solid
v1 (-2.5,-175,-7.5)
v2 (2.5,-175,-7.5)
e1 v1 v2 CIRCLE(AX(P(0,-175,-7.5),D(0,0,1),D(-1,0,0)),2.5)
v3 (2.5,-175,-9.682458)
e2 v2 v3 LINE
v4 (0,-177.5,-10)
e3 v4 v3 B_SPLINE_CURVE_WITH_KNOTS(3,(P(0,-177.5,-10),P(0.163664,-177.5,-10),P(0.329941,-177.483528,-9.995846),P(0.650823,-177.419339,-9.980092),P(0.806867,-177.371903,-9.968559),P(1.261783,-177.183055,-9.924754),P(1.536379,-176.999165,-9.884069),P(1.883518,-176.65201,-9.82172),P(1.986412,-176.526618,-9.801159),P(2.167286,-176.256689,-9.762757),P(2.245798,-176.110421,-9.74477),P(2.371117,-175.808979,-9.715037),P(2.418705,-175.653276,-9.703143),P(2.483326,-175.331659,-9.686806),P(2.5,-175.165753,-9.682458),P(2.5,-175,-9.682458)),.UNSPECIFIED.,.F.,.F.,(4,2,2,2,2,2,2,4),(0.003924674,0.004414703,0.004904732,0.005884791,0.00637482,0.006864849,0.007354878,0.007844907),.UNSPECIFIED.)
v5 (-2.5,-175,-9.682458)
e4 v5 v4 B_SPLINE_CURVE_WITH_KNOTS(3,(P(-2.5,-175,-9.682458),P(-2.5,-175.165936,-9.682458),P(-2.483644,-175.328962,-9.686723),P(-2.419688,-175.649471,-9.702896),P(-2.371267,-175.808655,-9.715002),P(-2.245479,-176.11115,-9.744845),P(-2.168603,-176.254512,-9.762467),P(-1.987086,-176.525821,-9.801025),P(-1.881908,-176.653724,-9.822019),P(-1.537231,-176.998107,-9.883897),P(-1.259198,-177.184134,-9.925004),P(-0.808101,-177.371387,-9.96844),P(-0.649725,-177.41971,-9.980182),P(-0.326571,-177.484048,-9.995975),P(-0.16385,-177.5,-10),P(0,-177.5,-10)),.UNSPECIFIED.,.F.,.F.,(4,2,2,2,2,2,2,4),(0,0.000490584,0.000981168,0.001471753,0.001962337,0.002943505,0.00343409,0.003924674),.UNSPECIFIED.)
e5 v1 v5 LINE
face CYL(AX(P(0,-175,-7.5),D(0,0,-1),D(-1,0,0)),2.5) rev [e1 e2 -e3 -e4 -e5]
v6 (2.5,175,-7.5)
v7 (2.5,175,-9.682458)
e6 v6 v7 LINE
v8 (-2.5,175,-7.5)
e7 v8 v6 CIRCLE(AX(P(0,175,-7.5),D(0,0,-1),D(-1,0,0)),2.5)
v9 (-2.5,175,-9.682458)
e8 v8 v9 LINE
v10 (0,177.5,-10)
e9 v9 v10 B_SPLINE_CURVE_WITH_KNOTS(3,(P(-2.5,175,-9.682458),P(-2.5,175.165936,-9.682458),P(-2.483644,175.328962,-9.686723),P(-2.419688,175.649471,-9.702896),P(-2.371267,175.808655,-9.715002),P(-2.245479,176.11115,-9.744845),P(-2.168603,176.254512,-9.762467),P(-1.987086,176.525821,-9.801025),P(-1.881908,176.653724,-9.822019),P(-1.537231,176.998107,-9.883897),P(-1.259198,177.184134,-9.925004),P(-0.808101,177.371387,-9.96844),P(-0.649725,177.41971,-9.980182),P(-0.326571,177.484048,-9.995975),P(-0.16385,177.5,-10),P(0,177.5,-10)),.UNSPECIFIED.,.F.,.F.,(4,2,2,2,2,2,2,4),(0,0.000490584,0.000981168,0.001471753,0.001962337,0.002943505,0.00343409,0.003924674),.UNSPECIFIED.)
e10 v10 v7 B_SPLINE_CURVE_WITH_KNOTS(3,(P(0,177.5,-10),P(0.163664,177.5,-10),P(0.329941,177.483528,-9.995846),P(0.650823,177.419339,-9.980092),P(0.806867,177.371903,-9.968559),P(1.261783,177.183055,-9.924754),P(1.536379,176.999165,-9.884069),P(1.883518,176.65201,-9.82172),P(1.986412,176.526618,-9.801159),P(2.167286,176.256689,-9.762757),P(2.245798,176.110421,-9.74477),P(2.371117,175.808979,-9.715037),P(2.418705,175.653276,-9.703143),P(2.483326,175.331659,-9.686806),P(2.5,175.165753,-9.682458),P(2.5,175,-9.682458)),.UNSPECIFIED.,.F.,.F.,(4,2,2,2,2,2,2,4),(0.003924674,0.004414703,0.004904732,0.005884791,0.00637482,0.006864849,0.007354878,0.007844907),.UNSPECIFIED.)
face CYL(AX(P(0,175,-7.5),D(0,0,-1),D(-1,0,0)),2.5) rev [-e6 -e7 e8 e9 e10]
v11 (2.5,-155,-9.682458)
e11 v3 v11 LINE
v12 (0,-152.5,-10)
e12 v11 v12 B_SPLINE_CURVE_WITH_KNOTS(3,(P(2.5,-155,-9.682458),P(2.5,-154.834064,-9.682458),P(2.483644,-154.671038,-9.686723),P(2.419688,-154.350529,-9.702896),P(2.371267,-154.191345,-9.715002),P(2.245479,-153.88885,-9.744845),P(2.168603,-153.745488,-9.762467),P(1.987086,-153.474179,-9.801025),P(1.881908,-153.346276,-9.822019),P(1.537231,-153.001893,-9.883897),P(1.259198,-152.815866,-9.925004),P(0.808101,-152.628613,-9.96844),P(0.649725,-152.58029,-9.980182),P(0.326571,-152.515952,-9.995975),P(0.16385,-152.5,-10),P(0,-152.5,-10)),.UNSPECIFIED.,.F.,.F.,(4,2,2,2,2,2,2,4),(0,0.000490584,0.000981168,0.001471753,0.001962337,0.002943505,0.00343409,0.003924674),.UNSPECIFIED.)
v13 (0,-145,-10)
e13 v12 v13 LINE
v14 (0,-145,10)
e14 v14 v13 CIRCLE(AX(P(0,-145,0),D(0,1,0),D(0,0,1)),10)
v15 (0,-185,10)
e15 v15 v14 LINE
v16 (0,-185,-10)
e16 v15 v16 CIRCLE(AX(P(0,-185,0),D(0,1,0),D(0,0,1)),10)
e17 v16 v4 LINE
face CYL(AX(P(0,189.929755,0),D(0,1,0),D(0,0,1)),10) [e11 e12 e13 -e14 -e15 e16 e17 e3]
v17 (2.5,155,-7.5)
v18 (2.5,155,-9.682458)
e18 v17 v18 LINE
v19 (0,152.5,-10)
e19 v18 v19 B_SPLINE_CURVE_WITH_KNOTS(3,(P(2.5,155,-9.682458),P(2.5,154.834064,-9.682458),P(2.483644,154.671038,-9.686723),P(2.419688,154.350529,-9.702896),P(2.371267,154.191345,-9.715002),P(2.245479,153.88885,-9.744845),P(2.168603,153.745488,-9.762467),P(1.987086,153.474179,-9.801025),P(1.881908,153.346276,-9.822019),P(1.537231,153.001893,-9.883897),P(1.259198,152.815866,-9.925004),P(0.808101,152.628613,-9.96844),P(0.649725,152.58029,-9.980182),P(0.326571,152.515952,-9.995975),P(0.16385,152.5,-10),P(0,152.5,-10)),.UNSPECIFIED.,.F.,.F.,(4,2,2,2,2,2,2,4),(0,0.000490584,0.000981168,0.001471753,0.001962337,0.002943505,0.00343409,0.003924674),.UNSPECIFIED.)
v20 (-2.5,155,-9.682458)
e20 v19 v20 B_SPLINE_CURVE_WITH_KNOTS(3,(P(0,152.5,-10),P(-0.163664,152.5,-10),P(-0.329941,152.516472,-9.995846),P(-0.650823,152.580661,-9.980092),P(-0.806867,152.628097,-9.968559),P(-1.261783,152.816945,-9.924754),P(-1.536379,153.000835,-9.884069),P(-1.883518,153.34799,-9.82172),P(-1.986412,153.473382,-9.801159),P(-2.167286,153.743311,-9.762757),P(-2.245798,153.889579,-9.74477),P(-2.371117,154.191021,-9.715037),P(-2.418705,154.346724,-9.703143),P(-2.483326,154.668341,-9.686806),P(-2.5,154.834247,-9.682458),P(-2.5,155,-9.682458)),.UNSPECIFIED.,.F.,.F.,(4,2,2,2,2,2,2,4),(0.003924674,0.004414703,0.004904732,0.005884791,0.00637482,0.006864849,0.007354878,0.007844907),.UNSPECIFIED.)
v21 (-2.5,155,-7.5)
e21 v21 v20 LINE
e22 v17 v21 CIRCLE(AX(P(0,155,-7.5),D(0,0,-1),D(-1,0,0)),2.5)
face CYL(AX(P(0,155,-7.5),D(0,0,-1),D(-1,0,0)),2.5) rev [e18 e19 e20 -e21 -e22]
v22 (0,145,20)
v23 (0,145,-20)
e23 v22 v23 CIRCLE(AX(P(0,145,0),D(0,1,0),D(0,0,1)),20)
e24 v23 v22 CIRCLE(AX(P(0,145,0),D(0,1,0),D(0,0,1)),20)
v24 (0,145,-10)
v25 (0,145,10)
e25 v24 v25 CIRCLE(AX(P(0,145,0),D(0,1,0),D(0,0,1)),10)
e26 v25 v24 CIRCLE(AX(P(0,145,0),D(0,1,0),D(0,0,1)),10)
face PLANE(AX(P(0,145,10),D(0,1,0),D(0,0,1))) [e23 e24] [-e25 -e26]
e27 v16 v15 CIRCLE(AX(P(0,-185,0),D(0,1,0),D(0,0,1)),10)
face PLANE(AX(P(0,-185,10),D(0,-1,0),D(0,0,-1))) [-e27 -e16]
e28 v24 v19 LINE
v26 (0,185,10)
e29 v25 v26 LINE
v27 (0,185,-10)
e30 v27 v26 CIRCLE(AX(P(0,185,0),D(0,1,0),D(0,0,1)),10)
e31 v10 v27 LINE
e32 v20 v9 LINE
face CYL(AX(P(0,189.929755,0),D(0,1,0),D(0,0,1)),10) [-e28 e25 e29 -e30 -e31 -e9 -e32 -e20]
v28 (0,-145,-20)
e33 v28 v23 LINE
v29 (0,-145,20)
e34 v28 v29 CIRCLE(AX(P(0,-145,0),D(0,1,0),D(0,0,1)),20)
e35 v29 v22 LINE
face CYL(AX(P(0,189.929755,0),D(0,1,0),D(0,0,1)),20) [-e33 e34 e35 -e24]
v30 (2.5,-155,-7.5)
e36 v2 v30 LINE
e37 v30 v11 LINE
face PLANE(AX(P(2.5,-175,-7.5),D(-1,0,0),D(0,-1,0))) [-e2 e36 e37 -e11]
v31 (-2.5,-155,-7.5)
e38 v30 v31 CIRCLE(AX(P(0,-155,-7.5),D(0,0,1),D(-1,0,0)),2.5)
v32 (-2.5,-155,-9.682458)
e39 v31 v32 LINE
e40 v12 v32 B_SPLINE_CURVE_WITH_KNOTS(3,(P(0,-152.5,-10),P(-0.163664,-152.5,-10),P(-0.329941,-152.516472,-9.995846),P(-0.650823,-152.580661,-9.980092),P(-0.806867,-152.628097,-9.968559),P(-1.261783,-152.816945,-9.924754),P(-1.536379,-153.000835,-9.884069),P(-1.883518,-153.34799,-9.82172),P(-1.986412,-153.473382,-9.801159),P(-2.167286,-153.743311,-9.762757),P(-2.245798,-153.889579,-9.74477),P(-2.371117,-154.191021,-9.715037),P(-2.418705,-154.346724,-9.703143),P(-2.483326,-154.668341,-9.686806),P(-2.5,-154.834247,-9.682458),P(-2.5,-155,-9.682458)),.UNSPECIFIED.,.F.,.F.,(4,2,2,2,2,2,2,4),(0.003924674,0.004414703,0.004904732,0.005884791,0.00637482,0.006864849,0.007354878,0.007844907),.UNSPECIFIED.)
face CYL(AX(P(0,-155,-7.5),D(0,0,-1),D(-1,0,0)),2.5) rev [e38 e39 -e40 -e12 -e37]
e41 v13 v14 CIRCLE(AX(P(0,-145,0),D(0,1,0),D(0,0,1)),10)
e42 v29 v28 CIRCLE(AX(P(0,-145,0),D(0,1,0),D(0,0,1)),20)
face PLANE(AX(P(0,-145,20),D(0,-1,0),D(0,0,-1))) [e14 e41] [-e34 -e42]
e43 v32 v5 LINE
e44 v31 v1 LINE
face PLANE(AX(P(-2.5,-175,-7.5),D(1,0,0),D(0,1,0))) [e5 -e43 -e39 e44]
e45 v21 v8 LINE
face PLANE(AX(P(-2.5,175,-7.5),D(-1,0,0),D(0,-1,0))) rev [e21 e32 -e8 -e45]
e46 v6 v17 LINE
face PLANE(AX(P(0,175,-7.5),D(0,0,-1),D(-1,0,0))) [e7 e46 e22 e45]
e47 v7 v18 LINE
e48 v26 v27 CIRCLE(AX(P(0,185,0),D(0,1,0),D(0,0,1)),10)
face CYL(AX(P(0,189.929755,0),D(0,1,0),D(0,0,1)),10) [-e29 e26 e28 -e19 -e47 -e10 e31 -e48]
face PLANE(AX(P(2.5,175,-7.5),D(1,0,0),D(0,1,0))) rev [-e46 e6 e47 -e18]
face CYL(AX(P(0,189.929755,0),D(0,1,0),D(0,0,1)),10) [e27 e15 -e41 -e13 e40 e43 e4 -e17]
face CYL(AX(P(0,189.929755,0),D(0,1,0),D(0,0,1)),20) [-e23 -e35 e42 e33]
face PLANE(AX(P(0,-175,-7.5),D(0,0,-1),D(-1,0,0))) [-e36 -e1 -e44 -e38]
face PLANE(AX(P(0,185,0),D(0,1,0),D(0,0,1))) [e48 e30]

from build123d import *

# Parameters (mm, degrees)
CUT_EXTRUDE1_DEPTH = 2.5


with BuildPart() as part:
    # Sketch1 → Revolve1 (revolve)
    with BuildSketch(Plane(origin=(0, 0, 0), x_dir=(0, 0, -1), z_dir=(1, 0, 0))):
        Polygon((0, 185), (-10, 185), (-10, 145), (-20, 145), (-20, -145), (-10, -145), (-10, -185), (0, -185), align=None)
    revolve(axis=Axis((0, 189.929754582, 0), (0, -1, 0)))

    # Sketch2 → Cut-Extrude1 (cut)
    with BuildSketch(Plane(origin=(0, 0, -10), x_dir=(-1, 0, 0), z_dir=(0, 0, -1))):
        with BuildLine():
            Line((2.5, 175), (2.5, 155))
            ThreePointArc((2.5, 155), (0, 152.5), (-2.5, 155))
            Line((-2.5, 155), (-2.5, 175))
            ThreePointArc((-2.5, 175), (0, 177.5), (2.5, 175))
        make_face()
    cut_extrude1 = extrude(amount=-CUT_EXTRUDE1_DEPTH, mode=Mode.SUBTRACT)

    # Mirror1: Cut-Extrude1 across plane
    add(cut_extrude1.mirror(Plane.ZX), mode=Mode.SUBTRACT)


solid = part.part
